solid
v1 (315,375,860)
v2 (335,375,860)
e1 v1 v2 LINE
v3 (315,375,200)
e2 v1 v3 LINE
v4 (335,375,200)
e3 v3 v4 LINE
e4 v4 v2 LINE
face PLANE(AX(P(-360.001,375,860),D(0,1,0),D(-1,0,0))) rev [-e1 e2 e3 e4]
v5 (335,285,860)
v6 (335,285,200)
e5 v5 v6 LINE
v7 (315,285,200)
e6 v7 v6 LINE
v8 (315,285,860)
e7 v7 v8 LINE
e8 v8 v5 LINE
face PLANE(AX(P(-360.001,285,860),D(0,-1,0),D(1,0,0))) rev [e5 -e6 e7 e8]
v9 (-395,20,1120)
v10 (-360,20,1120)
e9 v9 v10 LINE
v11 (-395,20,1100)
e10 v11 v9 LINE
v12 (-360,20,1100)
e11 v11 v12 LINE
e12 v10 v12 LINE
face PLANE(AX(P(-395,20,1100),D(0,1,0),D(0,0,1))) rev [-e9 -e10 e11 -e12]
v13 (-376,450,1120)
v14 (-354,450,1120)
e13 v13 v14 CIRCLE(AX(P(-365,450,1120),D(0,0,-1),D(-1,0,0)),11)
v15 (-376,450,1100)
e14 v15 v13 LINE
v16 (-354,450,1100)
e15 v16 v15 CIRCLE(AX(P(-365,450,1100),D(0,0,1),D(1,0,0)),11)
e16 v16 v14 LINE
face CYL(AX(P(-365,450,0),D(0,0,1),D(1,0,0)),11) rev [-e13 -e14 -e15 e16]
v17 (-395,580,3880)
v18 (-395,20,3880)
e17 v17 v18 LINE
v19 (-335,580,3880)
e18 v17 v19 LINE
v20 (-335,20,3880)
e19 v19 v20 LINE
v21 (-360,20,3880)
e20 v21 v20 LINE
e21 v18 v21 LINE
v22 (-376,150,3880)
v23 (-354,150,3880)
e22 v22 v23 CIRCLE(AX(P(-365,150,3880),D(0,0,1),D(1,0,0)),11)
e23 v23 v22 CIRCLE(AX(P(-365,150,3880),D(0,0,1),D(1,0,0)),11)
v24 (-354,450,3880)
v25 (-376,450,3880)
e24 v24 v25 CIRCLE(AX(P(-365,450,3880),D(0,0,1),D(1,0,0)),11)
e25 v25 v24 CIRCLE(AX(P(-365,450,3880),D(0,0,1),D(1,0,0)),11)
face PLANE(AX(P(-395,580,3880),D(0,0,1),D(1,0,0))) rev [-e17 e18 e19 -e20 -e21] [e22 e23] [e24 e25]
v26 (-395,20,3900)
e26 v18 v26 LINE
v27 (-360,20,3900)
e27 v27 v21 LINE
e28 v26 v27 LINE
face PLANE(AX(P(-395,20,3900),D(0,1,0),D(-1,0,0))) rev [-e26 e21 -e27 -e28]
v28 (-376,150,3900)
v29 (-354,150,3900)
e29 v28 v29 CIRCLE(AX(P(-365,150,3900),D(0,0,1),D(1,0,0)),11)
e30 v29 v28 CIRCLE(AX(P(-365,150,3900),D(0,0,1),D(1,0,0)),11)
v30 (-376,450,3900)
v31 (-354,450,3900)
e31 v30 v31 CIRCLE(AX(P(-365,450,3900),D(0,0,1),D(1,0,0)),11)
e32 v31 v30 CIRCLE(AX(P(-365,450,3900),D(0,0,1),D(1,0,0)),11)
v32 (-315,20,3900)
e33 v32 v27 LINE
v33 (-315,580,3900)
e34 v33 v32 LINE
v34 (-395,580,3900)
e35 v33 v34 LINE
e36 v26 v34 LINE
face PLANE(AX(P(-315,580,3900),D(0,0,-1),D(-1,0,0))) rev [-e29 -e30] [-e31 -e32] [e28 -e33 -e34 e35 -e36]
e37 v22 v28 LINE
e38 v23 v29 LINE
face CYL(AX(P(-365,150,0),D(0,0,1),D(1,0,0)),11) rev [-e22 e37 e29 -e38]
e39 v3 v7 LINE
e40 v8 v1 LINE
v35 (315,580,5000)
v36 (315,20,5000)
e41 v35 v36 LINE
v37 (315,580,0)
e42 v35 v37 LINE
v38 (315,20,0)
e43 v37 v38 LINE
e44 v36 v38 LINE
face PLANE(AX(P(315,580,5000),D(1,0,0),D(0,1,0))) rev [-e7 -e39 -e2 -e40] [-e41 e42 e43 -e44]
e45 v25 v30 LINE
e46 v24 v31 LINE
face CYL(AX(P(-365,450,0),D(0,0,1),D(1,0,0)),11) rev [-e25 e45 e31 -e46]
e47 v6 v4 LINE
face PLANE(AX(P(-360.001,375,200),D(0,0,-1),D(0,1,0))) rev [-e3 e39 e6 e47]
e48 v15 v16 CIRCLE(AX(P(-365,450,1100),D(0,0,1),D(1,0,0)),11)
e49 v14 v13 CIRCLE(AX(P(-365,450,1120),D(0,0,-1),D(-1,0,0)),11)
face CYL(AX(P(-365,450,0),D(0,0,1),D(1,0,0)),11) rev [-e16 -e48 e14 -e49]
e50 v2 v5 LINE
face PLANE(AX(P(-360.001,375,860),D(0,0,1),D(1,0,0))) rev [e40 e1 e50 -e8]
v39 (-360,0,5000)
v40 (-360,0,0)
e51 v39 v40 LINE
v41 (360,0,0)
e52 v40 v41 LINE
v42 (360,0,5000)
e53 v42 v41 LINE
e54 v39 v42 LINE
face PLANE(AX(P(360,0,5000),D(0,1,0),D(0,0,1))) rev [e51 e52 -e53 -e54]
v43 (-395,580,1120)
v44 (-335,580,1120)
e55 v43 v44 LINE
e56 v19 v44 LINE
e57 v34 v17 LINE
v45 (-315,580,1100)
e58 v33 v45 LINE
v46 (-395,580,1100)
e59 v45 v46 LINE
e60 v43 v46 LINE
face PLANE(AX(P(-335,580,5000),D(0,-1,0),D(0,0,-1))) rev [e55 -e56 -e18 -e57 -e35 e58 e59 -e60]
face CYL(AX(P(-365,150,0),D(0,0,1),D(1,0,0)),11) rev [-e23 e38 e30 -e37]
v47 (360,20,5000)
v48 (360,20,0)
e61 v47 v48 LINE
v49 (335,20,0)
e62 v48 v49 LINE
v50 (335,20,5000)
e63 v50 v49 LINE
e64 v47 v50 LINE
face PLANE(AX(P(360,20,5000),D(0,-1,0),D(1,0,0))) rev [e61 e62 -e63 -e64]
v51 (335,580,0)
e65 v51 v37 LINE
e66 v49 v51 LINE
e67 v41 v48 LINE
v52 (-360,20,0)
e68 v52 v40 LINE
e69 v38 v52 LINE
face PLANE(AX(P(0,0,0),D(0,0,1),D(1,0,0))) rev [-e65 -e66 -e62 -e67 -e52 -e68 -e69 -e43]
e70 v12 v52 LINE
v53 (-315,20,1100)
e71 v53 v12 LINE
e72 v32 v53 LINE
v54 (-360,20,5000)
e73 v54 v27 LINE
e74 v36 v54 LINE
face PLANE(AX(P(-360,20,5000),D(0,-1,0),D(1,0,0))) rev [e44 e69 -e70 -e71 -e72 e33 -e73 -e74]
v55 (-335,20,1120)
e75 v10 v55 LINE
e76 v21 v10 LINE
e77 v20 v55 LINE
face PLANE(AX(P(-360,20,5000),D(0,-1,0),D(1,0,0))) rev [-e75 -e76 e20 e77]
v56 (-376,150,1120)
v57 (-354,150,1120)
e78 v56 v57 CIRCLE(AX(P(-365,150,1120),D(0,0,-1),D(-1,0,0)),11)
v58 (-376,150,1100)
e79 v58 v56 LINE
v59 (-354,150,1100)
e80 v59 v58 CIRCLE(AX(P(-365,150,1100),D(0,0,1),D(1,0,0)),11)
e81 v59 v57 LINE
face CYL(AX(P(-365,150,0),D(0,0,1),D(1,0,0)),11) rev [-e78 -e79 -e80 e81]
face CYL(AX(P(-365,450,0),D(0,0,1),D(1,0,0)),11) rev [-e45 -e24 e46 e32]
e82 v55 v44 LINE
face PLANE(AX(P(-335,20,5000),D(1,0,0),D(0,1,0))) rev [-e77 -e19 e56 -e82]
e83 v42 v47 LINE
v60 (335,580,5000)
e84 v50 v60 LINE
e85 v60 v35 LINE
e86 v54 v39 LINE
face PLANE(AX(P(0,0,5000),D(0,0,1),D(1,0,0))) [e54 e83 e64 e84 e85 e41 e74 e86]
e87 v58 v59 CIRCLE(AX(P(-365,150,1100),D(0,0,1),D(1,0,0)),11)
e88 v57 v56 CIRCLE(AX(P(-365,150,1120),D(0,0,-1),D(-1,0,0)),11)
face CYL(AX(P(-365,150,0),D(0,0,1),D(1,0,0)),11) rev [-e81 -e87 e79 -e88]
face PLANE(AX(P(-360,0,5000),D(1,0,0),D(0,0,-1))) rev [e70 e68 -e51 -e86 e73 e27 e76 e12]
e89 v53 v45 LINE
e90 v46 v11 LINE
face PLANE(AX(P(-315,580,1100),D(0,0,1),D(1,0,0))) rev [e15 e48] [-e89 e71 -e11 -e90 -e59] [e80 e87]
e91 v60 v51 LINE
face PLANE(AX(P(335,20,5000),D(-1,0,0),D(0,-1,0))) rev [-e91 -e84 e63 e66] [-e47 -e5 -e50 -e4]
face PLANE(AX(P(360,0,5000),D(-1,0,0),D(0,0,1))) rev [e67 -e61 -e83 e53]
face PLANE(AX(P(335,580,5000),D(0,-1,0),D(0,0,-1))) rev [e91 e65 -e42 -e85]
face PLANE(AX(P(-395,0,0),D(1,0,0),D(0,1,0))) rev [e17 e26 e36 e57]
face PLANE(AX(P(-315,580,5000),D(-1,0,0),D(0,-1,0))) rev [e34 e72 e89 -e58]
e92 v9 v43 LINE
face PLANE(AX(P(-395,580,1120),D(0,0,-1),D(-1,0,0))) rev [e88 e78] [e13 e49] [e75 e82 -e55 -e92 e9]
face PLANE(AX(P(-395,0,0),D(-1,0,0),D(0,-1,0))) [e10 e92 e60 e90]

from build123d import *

# Parameters (mm, degrees)
BOSS_EXTRUDE1_DEPTH = 5000
CUT_EXTRUDE1_REACH  = 5083.282
SKETCH2_W           = 660
SKETCH2_H           = 90
SKETCH3_W           = 1100
SKETCH3_H           = 560
CUT_EXTRUDE2_DEPTH  = 20
SKETCH4_W           = 20
SKETCH4_H           = 560
BOSS_EXTRUDE2_DEPTH = 60
SKETCH5_R           = 11
CUT_EXTRUDE3_DEPTH  = 3963.628546811


with BuildPart() as part:
    # Sketch1 → Boss-Extrude1 (new body)
    with BuildSketch(Plane.XY):
        Polygon((360, 0), (-360, 0), (-360, 20), (-335, 20), (-335, 580), (-315, 580), (-315, 20), (315, 20), (315, 580), (335, 580), (335, 20), (360, 20), align=None)
    extrude(amount=BOSS_EXTRUDE1_DEPTH)

    # Sketch2 → Cut-Extrude1 (cut, up to next)
    with BuildSketch(Plane(origin=(335, 0, 0), x_dir=(0, 0, -1), z_dir=(1, 0, 0)), mode=Mode.PRIVATE) as cut_extrude1_sk1:
        with Locations((-530, 330)):
            Rectangle(SKETCH2_W, SKETCH2_H)
    cut_extrude1_tool1 = extrude(cut_extrude1_sk1.sketch, amount=-CUT_EXTRUDE1_REACH, mode=Mode.PRIVATE) & part.part
    add(cut_extrude1_tool1.solids().sort_by_distance((335, 330, 530))[0], mode=Mode.SUBTRACT)

    # Sketch3 → Cut-Extrude2 (cut)
    with BuildSketch(Plane.ZY.offset(335)):
        with Locations((4450, 300)):
            Rectangle(SKETCH3_W, SKETCH3_H)
        with Locations((550, 300)):
            Rectangle(SKETCH3_W, SKETCH3_H)
    extrude(amount=-CUT_EXTRUDE2_DEPTH, mode=Mode.SUBTRACT)

    # Sketch4 → Boss-Extrude2 (add)
    with BuildSketch(Plane.ZY.offset(335)):
        with Locations((1110, 300)):
            Rectangle(SKETCH4_W, SKETCH4_H)
        with Locations((3890, 300)):
            Rectangle(SKETCH4_W, SKETCH4_H)
    extrude(amount=BOSS_EXTRUDE2_DEPTH)

    # Sketch5 → Cut-Extrude3 (cut, through all)
    with BuildSketch(Plane.XY.offset(3900)):
        with Locations((-365, 450)):
            Circle(SKETCH5_R)
        with Locations((-365, 150)):
            Circle(SKETCH5_R)
    extrude(amount=-CUT_EXTRUDE3_DEPTH, mode=Mode.SUBTRACT)


solid = part.part
